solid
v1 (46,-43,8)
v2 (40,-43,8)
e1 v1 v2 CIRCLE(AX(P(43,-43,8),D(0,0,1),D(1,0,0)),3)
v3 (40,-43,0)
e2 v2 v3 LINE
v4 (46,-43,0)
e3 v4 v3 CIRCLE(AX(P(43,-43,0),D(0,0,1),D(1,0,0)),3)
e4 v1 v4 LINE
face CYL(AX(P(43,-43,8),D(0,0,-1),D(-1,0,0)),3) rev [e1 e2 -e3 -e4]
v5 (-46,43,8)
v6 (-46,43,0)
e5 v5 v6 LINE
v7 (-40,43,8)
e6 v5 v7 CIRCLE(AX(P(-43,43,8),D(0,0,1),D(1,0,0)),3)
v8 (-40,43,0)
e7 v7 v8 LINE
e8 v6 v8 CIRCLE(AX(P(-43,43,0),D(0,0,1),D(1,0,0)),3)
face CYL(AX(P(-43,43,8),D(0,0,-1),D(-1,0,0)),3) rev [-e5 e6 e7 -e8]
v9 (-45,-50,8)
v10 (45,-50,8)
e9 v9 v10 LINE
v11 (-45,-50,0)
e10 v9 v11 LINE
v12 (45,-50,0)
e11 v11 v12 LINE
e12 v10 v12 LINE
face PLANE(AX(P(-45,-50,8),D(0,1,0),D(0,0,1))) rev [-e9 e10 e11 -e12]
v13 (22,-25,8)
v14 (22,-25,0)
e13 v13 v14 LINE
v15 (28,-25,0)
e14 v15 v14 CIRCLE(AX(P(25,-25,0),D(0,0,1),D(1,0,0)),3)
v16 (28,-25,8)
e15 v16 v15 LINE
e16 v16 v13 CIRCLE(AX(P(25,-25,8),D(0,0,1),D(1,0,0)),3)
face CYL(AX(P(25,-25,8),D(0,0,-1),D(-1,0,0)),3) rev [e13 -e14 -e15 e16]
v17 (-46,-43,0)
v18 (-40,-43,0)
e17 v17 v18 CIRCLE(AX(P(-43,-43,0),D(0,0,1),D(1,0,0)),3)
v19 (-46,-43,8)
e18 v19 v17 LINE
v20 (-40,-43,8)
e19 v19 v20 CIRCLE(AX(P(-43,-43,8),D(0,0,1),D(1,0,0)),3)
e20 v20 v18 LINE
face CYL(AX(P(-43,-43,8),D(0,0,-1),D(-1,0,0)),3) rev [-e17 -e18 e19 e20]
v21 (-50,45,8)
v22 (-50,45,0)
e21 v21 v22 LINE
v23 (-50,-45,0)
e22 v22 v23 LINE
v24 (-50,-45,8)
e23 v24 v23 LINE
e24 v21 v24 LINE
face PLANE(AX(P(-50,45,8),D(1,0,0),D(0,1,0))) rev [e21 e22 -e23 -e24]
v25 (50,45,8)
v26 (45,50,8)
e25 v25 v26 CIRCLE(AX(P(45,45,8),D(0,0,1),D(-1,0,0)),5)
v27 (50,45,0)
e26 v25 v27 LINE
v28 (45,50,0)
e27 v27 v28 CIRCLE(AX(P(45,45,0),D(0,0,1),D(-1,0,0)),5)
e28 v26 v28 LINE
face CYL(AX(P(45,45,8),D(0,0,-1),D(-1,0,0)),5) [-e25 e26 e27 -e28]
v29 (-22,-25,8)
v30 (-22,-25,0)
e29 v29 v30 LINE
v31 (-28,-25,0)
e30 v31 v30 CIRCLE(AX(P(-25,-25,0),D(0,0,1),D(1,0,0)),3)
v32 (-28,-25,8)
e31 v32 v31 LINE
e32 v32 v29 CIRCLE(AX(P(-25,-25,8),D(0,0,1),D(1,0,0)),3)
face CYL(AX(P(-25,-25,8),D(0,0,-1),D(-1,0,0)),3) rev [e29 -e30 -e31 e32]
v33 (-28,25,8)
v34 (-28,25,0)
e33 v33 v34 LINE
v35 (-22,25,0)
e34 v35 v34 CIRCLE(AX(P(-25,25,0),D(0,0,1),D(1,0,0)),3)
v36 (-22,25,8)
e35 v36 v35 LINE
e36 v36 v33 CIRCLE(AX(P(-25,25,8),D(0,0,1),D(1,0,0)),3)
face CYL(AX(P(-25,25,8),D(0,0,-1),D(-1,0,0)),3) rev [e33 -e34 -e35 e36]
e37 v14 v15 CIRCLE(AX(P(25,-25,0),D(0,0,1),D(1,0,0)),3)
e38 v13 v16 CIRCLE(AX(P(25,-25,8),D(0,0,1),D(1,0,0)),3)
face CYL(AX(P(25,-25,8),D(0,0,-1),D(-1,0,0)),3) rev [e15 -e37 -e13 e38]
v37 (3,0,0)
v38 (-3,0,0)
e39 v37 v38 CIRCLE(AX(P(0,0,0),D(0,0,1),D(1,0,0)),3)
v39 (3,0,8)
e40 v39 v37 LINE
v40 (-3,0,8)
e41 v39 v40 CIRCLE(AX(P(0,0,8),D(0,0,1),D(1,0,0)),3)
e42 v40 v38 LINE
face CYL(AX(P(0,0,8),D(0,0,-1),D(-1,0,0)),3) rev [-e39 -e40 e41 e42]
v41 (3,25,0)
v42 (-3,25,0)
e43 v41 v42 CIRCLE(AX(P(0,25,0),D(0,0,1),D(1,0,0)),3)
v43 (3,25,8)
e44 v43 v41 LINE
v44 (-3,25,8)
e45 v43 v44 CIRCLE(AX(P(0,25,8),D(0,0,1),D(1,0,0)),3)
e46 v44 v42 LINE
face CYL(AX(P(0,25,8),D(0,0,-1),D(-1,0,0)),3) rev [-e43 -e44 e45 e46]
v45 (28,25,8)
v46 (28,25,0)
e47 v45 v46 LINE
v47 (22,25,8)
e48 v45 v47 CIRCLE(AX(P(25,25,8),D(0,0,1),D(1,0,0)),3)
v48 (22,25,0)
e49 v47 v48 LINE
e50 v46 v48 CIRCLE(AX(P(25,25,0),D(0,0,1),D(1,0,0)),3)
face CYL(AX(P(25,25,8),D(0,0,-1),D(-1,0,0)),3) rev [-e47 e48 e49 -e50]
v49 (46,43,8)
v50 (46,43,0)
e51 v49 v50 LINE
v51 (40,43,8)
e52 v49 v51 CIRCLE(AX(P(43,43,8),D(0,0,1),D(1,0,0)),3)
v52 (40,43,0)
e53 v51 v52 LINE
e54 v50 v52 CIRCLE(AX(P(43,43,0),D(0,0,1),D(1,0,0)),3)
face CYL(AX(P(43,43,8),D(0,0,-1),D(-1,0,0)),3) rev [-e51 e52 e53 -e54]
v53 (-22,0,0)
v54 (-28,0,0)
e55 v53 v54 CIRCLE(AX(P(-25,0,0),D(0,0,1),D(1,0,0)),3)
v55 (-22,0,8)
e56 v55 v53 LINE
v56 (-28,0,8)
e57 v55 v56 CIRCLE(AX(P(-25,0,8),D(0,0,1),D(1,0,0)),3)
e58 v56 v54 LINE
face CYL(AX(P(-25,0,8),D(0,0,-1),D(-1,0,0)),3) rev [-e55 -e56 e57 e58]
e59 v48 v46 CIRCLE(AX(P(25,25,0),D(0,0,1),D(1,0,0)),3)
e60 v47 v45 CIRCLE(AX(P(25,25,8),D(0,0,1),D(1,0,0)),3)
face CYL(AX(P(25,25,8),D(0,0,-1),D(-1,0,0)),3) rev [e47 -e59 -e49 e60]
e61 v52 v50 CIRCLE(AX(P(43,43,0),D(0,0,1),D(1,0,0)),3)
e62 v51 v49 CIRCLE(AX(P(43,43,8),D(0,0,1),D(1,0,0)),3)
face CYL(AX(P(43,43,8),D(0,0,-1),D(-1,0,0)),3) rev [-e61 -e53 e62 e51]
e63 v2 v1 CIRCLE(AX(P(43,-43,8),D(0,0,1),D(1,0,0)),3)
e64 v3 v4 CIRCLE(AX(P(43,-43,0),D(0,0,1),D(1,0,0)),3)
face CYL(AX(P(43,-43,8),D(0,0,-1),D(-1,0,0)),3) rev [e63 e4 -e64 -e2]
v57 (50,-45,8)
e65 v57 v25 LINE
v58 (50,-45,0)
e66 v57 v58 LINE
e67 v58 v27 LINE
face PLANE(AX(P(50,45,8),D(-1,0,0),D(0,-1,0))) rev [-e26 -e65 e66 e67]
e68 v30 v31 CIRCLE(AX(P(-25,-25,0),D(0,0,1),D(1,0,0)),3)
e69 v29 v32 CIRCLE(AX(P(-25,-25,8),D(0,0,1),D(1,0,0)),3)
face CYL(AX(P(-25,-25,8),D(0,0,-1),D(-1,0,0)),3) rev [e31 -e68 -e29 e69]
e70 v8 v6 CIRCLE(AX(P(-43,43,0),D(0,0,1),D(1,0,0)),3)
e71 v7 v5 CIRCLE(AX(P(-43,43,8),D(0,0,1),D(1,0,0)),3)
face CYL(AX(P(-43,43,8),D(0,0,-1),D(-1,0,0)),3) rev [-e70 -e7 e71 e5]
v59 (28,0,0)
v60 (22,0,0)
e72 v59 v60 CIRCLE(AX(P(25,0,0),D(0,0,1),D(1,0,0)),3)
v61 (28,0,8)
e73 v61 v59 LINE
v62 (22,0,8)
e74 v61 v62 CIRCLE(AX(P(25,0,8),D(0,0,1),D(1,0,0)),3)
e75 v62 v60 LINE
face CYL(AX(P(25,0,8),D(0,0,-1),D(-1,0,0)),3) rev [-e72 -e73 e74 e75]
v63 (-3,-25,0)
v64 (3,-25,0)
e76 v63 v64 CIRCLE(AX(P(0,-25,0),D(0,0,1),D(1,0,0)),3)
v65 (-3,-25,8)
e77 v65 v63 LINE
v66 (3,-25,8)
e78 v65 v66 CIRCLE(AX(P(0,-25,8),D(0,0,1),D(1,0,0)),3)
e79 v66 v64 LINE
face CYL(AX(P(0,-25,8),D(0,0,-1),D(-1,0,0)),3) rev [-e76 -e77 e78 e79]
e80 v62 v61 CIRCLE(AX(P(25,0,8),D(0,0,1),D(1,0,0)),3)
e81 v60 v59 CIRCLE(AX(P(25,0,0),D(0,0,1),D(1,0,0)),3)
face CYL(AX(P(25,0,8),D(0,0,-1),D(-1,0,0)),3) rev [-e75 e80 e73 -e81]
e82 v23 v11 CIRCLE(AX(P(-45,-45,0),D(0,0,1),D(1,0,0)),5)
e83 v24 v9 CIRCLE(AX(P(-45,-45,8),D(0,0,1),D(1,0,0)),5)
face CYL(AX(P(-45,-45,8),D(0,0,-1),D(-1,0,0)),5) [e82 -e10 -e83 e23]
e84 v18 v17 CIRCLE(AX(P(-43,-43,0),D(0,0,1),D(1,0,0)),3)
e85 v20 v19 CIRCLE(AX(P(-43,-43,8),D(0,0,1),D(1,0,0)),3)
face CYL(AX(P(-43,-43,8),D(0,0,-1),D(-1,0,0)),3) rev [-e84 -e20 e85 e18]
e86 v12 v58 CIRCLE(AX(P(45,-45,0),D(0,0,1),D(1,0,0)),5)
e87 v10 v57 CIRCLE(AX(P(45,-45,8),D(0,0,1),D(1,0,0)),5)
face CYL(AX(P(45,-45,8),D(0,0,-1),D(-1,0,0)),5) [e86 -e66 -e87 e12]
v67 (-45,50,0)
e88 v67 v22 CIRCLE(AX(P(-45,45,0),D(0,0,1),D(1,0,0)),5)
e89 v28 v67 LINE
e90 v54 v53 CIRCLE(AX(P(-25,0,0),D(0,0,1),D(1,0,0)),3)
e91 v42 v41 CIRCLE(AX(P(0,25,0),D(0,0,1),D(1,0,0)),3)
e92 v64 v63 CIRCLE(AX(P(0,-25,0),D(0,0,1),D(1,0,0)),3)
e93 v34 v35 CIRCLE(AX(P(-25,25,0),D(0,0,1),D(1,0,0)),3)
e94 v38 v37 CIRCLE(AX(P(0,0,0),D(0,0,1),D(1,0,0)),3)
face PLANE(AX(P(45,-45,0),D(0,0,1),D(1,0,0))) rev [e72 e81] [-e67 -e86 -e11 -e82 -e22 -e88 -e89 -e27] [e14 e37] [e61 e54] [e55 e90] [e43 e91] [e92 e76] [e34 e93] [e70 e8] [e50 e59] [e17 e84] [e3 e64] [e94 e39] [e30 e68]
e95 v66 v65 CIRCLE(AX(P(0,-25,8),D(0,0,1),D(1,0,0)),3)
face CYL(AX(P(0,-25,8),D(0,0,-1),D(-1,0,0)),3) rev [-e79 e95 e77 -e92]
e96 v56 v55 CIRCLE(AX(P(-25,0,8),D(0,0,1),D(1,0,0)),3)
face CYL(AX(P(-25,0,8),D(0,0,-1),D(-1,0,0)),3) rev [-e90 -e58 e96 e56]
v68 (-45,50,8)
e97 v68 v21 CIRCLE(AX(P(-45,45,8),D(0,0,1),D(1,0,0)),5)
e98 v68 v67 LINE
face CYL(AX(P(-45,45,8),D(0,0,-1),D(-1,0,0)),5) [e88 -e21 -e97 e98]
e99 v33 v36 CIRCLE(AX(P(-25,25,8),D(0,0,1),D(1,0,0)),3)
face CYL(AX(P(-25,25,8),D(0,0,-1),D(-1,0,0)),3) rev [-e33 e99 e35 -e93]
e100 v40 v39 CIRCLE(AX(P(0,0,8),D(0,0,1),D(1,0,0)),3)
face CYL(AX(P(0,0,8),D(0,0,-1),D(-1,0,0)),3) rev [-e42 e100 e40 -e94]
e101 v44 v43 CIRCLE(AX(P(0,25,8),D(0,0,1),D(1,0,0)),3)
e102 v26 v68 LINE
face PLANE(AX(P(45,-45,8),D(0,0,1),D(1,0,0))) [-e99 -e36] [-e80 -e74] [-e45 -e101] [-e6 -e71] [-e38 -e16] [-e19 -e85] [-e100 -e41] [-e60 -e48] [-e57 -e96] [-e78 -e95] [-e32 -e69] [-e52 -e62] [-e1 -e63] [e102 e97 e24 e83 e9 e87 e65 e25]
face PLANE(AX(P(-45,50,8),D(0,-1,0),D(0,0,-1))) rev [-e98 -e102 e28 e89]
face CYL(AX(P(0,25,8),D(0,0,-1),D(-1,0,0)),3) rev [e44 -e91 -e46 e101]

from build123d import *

# Parameters (mm, degrees)
SKETCH1_R           = 3
BOSS_EXTRUDE1_DEPTH = 8


with BuildPart() as part:
    # Sketch1 → Boss-Extrude1 (new body)
    with BuildSketch(Plane.XY):
        with BuildLine():
            Line((-45, 50), (45, 50))
            ThreePointArc((45, 50), (48.535533906, 48.535533906), (50, 45))
            Line((50, 45), (50, -45))
            ThreePointArc((50, -45), (48.535533906, -48.535533906), (45, -50))
            Line((45, -50), (-45, -50))
            ThreePointArc((-45, -50), (-48.535533906, -48.535533906), (-50, -45))
            Line((-50, -45), (-50, 45))
            ThreePointArc((-50, 45), (-48.535533906, 48.535533906), (-45, 50))
        make_face()
        with Locations((-25, 25)):
            Circle(SKETCH1_R, mode=Mode.SUBTRACT)
        with Locations((0, 25)):
            Circle(SKETCH1_R, mode=Mode.SUBTRACT)
        with Locations((25, 25)):
            Circle(SKETCH1_R, mode=Mode.SUBTRACT)
        Circle(SKETCH1_R, mode=Mode.SUBTRACT)
        with Locations((25, 0)):
            Circle(SKETCH1_R, mode=Mode.SUBTRACT)
        with Locations((0, -25)):
            Circle(SKETCH1_R, mode=Mode.SUBTRACT)
        with Locations((25, -25)):
            Circle(SKETCH1_R, mode=Mode.SUBTRACT)
        with Locations((-25, 0)):
            Circle(SKETCH1_R, mode=Mode.SUBTRACT)
        with Locations((-25, -25)):
            Circle(SKETCH1_R, mode=Mode.SUBTRACT)
        with Locations((43, 43)):
            Circle(SKETCH1_R, mode=Mode.SUBTRACT)
        with Locations((43, -43)):
            Circle(SKETCH1_R, mode=Mode.SUBTRACT)
        with Locations((-43, -43)):
            Circle(SKETCH1_R, mode=Mode.SUBTRACT)
        with Locations((-43, 43)):
            Circle(SKETCH1_R, mode=Mode.SUBTRACT)
    extrude(amount=BOSS_EXTRUDE1_DEPTH)


solid = part.part
